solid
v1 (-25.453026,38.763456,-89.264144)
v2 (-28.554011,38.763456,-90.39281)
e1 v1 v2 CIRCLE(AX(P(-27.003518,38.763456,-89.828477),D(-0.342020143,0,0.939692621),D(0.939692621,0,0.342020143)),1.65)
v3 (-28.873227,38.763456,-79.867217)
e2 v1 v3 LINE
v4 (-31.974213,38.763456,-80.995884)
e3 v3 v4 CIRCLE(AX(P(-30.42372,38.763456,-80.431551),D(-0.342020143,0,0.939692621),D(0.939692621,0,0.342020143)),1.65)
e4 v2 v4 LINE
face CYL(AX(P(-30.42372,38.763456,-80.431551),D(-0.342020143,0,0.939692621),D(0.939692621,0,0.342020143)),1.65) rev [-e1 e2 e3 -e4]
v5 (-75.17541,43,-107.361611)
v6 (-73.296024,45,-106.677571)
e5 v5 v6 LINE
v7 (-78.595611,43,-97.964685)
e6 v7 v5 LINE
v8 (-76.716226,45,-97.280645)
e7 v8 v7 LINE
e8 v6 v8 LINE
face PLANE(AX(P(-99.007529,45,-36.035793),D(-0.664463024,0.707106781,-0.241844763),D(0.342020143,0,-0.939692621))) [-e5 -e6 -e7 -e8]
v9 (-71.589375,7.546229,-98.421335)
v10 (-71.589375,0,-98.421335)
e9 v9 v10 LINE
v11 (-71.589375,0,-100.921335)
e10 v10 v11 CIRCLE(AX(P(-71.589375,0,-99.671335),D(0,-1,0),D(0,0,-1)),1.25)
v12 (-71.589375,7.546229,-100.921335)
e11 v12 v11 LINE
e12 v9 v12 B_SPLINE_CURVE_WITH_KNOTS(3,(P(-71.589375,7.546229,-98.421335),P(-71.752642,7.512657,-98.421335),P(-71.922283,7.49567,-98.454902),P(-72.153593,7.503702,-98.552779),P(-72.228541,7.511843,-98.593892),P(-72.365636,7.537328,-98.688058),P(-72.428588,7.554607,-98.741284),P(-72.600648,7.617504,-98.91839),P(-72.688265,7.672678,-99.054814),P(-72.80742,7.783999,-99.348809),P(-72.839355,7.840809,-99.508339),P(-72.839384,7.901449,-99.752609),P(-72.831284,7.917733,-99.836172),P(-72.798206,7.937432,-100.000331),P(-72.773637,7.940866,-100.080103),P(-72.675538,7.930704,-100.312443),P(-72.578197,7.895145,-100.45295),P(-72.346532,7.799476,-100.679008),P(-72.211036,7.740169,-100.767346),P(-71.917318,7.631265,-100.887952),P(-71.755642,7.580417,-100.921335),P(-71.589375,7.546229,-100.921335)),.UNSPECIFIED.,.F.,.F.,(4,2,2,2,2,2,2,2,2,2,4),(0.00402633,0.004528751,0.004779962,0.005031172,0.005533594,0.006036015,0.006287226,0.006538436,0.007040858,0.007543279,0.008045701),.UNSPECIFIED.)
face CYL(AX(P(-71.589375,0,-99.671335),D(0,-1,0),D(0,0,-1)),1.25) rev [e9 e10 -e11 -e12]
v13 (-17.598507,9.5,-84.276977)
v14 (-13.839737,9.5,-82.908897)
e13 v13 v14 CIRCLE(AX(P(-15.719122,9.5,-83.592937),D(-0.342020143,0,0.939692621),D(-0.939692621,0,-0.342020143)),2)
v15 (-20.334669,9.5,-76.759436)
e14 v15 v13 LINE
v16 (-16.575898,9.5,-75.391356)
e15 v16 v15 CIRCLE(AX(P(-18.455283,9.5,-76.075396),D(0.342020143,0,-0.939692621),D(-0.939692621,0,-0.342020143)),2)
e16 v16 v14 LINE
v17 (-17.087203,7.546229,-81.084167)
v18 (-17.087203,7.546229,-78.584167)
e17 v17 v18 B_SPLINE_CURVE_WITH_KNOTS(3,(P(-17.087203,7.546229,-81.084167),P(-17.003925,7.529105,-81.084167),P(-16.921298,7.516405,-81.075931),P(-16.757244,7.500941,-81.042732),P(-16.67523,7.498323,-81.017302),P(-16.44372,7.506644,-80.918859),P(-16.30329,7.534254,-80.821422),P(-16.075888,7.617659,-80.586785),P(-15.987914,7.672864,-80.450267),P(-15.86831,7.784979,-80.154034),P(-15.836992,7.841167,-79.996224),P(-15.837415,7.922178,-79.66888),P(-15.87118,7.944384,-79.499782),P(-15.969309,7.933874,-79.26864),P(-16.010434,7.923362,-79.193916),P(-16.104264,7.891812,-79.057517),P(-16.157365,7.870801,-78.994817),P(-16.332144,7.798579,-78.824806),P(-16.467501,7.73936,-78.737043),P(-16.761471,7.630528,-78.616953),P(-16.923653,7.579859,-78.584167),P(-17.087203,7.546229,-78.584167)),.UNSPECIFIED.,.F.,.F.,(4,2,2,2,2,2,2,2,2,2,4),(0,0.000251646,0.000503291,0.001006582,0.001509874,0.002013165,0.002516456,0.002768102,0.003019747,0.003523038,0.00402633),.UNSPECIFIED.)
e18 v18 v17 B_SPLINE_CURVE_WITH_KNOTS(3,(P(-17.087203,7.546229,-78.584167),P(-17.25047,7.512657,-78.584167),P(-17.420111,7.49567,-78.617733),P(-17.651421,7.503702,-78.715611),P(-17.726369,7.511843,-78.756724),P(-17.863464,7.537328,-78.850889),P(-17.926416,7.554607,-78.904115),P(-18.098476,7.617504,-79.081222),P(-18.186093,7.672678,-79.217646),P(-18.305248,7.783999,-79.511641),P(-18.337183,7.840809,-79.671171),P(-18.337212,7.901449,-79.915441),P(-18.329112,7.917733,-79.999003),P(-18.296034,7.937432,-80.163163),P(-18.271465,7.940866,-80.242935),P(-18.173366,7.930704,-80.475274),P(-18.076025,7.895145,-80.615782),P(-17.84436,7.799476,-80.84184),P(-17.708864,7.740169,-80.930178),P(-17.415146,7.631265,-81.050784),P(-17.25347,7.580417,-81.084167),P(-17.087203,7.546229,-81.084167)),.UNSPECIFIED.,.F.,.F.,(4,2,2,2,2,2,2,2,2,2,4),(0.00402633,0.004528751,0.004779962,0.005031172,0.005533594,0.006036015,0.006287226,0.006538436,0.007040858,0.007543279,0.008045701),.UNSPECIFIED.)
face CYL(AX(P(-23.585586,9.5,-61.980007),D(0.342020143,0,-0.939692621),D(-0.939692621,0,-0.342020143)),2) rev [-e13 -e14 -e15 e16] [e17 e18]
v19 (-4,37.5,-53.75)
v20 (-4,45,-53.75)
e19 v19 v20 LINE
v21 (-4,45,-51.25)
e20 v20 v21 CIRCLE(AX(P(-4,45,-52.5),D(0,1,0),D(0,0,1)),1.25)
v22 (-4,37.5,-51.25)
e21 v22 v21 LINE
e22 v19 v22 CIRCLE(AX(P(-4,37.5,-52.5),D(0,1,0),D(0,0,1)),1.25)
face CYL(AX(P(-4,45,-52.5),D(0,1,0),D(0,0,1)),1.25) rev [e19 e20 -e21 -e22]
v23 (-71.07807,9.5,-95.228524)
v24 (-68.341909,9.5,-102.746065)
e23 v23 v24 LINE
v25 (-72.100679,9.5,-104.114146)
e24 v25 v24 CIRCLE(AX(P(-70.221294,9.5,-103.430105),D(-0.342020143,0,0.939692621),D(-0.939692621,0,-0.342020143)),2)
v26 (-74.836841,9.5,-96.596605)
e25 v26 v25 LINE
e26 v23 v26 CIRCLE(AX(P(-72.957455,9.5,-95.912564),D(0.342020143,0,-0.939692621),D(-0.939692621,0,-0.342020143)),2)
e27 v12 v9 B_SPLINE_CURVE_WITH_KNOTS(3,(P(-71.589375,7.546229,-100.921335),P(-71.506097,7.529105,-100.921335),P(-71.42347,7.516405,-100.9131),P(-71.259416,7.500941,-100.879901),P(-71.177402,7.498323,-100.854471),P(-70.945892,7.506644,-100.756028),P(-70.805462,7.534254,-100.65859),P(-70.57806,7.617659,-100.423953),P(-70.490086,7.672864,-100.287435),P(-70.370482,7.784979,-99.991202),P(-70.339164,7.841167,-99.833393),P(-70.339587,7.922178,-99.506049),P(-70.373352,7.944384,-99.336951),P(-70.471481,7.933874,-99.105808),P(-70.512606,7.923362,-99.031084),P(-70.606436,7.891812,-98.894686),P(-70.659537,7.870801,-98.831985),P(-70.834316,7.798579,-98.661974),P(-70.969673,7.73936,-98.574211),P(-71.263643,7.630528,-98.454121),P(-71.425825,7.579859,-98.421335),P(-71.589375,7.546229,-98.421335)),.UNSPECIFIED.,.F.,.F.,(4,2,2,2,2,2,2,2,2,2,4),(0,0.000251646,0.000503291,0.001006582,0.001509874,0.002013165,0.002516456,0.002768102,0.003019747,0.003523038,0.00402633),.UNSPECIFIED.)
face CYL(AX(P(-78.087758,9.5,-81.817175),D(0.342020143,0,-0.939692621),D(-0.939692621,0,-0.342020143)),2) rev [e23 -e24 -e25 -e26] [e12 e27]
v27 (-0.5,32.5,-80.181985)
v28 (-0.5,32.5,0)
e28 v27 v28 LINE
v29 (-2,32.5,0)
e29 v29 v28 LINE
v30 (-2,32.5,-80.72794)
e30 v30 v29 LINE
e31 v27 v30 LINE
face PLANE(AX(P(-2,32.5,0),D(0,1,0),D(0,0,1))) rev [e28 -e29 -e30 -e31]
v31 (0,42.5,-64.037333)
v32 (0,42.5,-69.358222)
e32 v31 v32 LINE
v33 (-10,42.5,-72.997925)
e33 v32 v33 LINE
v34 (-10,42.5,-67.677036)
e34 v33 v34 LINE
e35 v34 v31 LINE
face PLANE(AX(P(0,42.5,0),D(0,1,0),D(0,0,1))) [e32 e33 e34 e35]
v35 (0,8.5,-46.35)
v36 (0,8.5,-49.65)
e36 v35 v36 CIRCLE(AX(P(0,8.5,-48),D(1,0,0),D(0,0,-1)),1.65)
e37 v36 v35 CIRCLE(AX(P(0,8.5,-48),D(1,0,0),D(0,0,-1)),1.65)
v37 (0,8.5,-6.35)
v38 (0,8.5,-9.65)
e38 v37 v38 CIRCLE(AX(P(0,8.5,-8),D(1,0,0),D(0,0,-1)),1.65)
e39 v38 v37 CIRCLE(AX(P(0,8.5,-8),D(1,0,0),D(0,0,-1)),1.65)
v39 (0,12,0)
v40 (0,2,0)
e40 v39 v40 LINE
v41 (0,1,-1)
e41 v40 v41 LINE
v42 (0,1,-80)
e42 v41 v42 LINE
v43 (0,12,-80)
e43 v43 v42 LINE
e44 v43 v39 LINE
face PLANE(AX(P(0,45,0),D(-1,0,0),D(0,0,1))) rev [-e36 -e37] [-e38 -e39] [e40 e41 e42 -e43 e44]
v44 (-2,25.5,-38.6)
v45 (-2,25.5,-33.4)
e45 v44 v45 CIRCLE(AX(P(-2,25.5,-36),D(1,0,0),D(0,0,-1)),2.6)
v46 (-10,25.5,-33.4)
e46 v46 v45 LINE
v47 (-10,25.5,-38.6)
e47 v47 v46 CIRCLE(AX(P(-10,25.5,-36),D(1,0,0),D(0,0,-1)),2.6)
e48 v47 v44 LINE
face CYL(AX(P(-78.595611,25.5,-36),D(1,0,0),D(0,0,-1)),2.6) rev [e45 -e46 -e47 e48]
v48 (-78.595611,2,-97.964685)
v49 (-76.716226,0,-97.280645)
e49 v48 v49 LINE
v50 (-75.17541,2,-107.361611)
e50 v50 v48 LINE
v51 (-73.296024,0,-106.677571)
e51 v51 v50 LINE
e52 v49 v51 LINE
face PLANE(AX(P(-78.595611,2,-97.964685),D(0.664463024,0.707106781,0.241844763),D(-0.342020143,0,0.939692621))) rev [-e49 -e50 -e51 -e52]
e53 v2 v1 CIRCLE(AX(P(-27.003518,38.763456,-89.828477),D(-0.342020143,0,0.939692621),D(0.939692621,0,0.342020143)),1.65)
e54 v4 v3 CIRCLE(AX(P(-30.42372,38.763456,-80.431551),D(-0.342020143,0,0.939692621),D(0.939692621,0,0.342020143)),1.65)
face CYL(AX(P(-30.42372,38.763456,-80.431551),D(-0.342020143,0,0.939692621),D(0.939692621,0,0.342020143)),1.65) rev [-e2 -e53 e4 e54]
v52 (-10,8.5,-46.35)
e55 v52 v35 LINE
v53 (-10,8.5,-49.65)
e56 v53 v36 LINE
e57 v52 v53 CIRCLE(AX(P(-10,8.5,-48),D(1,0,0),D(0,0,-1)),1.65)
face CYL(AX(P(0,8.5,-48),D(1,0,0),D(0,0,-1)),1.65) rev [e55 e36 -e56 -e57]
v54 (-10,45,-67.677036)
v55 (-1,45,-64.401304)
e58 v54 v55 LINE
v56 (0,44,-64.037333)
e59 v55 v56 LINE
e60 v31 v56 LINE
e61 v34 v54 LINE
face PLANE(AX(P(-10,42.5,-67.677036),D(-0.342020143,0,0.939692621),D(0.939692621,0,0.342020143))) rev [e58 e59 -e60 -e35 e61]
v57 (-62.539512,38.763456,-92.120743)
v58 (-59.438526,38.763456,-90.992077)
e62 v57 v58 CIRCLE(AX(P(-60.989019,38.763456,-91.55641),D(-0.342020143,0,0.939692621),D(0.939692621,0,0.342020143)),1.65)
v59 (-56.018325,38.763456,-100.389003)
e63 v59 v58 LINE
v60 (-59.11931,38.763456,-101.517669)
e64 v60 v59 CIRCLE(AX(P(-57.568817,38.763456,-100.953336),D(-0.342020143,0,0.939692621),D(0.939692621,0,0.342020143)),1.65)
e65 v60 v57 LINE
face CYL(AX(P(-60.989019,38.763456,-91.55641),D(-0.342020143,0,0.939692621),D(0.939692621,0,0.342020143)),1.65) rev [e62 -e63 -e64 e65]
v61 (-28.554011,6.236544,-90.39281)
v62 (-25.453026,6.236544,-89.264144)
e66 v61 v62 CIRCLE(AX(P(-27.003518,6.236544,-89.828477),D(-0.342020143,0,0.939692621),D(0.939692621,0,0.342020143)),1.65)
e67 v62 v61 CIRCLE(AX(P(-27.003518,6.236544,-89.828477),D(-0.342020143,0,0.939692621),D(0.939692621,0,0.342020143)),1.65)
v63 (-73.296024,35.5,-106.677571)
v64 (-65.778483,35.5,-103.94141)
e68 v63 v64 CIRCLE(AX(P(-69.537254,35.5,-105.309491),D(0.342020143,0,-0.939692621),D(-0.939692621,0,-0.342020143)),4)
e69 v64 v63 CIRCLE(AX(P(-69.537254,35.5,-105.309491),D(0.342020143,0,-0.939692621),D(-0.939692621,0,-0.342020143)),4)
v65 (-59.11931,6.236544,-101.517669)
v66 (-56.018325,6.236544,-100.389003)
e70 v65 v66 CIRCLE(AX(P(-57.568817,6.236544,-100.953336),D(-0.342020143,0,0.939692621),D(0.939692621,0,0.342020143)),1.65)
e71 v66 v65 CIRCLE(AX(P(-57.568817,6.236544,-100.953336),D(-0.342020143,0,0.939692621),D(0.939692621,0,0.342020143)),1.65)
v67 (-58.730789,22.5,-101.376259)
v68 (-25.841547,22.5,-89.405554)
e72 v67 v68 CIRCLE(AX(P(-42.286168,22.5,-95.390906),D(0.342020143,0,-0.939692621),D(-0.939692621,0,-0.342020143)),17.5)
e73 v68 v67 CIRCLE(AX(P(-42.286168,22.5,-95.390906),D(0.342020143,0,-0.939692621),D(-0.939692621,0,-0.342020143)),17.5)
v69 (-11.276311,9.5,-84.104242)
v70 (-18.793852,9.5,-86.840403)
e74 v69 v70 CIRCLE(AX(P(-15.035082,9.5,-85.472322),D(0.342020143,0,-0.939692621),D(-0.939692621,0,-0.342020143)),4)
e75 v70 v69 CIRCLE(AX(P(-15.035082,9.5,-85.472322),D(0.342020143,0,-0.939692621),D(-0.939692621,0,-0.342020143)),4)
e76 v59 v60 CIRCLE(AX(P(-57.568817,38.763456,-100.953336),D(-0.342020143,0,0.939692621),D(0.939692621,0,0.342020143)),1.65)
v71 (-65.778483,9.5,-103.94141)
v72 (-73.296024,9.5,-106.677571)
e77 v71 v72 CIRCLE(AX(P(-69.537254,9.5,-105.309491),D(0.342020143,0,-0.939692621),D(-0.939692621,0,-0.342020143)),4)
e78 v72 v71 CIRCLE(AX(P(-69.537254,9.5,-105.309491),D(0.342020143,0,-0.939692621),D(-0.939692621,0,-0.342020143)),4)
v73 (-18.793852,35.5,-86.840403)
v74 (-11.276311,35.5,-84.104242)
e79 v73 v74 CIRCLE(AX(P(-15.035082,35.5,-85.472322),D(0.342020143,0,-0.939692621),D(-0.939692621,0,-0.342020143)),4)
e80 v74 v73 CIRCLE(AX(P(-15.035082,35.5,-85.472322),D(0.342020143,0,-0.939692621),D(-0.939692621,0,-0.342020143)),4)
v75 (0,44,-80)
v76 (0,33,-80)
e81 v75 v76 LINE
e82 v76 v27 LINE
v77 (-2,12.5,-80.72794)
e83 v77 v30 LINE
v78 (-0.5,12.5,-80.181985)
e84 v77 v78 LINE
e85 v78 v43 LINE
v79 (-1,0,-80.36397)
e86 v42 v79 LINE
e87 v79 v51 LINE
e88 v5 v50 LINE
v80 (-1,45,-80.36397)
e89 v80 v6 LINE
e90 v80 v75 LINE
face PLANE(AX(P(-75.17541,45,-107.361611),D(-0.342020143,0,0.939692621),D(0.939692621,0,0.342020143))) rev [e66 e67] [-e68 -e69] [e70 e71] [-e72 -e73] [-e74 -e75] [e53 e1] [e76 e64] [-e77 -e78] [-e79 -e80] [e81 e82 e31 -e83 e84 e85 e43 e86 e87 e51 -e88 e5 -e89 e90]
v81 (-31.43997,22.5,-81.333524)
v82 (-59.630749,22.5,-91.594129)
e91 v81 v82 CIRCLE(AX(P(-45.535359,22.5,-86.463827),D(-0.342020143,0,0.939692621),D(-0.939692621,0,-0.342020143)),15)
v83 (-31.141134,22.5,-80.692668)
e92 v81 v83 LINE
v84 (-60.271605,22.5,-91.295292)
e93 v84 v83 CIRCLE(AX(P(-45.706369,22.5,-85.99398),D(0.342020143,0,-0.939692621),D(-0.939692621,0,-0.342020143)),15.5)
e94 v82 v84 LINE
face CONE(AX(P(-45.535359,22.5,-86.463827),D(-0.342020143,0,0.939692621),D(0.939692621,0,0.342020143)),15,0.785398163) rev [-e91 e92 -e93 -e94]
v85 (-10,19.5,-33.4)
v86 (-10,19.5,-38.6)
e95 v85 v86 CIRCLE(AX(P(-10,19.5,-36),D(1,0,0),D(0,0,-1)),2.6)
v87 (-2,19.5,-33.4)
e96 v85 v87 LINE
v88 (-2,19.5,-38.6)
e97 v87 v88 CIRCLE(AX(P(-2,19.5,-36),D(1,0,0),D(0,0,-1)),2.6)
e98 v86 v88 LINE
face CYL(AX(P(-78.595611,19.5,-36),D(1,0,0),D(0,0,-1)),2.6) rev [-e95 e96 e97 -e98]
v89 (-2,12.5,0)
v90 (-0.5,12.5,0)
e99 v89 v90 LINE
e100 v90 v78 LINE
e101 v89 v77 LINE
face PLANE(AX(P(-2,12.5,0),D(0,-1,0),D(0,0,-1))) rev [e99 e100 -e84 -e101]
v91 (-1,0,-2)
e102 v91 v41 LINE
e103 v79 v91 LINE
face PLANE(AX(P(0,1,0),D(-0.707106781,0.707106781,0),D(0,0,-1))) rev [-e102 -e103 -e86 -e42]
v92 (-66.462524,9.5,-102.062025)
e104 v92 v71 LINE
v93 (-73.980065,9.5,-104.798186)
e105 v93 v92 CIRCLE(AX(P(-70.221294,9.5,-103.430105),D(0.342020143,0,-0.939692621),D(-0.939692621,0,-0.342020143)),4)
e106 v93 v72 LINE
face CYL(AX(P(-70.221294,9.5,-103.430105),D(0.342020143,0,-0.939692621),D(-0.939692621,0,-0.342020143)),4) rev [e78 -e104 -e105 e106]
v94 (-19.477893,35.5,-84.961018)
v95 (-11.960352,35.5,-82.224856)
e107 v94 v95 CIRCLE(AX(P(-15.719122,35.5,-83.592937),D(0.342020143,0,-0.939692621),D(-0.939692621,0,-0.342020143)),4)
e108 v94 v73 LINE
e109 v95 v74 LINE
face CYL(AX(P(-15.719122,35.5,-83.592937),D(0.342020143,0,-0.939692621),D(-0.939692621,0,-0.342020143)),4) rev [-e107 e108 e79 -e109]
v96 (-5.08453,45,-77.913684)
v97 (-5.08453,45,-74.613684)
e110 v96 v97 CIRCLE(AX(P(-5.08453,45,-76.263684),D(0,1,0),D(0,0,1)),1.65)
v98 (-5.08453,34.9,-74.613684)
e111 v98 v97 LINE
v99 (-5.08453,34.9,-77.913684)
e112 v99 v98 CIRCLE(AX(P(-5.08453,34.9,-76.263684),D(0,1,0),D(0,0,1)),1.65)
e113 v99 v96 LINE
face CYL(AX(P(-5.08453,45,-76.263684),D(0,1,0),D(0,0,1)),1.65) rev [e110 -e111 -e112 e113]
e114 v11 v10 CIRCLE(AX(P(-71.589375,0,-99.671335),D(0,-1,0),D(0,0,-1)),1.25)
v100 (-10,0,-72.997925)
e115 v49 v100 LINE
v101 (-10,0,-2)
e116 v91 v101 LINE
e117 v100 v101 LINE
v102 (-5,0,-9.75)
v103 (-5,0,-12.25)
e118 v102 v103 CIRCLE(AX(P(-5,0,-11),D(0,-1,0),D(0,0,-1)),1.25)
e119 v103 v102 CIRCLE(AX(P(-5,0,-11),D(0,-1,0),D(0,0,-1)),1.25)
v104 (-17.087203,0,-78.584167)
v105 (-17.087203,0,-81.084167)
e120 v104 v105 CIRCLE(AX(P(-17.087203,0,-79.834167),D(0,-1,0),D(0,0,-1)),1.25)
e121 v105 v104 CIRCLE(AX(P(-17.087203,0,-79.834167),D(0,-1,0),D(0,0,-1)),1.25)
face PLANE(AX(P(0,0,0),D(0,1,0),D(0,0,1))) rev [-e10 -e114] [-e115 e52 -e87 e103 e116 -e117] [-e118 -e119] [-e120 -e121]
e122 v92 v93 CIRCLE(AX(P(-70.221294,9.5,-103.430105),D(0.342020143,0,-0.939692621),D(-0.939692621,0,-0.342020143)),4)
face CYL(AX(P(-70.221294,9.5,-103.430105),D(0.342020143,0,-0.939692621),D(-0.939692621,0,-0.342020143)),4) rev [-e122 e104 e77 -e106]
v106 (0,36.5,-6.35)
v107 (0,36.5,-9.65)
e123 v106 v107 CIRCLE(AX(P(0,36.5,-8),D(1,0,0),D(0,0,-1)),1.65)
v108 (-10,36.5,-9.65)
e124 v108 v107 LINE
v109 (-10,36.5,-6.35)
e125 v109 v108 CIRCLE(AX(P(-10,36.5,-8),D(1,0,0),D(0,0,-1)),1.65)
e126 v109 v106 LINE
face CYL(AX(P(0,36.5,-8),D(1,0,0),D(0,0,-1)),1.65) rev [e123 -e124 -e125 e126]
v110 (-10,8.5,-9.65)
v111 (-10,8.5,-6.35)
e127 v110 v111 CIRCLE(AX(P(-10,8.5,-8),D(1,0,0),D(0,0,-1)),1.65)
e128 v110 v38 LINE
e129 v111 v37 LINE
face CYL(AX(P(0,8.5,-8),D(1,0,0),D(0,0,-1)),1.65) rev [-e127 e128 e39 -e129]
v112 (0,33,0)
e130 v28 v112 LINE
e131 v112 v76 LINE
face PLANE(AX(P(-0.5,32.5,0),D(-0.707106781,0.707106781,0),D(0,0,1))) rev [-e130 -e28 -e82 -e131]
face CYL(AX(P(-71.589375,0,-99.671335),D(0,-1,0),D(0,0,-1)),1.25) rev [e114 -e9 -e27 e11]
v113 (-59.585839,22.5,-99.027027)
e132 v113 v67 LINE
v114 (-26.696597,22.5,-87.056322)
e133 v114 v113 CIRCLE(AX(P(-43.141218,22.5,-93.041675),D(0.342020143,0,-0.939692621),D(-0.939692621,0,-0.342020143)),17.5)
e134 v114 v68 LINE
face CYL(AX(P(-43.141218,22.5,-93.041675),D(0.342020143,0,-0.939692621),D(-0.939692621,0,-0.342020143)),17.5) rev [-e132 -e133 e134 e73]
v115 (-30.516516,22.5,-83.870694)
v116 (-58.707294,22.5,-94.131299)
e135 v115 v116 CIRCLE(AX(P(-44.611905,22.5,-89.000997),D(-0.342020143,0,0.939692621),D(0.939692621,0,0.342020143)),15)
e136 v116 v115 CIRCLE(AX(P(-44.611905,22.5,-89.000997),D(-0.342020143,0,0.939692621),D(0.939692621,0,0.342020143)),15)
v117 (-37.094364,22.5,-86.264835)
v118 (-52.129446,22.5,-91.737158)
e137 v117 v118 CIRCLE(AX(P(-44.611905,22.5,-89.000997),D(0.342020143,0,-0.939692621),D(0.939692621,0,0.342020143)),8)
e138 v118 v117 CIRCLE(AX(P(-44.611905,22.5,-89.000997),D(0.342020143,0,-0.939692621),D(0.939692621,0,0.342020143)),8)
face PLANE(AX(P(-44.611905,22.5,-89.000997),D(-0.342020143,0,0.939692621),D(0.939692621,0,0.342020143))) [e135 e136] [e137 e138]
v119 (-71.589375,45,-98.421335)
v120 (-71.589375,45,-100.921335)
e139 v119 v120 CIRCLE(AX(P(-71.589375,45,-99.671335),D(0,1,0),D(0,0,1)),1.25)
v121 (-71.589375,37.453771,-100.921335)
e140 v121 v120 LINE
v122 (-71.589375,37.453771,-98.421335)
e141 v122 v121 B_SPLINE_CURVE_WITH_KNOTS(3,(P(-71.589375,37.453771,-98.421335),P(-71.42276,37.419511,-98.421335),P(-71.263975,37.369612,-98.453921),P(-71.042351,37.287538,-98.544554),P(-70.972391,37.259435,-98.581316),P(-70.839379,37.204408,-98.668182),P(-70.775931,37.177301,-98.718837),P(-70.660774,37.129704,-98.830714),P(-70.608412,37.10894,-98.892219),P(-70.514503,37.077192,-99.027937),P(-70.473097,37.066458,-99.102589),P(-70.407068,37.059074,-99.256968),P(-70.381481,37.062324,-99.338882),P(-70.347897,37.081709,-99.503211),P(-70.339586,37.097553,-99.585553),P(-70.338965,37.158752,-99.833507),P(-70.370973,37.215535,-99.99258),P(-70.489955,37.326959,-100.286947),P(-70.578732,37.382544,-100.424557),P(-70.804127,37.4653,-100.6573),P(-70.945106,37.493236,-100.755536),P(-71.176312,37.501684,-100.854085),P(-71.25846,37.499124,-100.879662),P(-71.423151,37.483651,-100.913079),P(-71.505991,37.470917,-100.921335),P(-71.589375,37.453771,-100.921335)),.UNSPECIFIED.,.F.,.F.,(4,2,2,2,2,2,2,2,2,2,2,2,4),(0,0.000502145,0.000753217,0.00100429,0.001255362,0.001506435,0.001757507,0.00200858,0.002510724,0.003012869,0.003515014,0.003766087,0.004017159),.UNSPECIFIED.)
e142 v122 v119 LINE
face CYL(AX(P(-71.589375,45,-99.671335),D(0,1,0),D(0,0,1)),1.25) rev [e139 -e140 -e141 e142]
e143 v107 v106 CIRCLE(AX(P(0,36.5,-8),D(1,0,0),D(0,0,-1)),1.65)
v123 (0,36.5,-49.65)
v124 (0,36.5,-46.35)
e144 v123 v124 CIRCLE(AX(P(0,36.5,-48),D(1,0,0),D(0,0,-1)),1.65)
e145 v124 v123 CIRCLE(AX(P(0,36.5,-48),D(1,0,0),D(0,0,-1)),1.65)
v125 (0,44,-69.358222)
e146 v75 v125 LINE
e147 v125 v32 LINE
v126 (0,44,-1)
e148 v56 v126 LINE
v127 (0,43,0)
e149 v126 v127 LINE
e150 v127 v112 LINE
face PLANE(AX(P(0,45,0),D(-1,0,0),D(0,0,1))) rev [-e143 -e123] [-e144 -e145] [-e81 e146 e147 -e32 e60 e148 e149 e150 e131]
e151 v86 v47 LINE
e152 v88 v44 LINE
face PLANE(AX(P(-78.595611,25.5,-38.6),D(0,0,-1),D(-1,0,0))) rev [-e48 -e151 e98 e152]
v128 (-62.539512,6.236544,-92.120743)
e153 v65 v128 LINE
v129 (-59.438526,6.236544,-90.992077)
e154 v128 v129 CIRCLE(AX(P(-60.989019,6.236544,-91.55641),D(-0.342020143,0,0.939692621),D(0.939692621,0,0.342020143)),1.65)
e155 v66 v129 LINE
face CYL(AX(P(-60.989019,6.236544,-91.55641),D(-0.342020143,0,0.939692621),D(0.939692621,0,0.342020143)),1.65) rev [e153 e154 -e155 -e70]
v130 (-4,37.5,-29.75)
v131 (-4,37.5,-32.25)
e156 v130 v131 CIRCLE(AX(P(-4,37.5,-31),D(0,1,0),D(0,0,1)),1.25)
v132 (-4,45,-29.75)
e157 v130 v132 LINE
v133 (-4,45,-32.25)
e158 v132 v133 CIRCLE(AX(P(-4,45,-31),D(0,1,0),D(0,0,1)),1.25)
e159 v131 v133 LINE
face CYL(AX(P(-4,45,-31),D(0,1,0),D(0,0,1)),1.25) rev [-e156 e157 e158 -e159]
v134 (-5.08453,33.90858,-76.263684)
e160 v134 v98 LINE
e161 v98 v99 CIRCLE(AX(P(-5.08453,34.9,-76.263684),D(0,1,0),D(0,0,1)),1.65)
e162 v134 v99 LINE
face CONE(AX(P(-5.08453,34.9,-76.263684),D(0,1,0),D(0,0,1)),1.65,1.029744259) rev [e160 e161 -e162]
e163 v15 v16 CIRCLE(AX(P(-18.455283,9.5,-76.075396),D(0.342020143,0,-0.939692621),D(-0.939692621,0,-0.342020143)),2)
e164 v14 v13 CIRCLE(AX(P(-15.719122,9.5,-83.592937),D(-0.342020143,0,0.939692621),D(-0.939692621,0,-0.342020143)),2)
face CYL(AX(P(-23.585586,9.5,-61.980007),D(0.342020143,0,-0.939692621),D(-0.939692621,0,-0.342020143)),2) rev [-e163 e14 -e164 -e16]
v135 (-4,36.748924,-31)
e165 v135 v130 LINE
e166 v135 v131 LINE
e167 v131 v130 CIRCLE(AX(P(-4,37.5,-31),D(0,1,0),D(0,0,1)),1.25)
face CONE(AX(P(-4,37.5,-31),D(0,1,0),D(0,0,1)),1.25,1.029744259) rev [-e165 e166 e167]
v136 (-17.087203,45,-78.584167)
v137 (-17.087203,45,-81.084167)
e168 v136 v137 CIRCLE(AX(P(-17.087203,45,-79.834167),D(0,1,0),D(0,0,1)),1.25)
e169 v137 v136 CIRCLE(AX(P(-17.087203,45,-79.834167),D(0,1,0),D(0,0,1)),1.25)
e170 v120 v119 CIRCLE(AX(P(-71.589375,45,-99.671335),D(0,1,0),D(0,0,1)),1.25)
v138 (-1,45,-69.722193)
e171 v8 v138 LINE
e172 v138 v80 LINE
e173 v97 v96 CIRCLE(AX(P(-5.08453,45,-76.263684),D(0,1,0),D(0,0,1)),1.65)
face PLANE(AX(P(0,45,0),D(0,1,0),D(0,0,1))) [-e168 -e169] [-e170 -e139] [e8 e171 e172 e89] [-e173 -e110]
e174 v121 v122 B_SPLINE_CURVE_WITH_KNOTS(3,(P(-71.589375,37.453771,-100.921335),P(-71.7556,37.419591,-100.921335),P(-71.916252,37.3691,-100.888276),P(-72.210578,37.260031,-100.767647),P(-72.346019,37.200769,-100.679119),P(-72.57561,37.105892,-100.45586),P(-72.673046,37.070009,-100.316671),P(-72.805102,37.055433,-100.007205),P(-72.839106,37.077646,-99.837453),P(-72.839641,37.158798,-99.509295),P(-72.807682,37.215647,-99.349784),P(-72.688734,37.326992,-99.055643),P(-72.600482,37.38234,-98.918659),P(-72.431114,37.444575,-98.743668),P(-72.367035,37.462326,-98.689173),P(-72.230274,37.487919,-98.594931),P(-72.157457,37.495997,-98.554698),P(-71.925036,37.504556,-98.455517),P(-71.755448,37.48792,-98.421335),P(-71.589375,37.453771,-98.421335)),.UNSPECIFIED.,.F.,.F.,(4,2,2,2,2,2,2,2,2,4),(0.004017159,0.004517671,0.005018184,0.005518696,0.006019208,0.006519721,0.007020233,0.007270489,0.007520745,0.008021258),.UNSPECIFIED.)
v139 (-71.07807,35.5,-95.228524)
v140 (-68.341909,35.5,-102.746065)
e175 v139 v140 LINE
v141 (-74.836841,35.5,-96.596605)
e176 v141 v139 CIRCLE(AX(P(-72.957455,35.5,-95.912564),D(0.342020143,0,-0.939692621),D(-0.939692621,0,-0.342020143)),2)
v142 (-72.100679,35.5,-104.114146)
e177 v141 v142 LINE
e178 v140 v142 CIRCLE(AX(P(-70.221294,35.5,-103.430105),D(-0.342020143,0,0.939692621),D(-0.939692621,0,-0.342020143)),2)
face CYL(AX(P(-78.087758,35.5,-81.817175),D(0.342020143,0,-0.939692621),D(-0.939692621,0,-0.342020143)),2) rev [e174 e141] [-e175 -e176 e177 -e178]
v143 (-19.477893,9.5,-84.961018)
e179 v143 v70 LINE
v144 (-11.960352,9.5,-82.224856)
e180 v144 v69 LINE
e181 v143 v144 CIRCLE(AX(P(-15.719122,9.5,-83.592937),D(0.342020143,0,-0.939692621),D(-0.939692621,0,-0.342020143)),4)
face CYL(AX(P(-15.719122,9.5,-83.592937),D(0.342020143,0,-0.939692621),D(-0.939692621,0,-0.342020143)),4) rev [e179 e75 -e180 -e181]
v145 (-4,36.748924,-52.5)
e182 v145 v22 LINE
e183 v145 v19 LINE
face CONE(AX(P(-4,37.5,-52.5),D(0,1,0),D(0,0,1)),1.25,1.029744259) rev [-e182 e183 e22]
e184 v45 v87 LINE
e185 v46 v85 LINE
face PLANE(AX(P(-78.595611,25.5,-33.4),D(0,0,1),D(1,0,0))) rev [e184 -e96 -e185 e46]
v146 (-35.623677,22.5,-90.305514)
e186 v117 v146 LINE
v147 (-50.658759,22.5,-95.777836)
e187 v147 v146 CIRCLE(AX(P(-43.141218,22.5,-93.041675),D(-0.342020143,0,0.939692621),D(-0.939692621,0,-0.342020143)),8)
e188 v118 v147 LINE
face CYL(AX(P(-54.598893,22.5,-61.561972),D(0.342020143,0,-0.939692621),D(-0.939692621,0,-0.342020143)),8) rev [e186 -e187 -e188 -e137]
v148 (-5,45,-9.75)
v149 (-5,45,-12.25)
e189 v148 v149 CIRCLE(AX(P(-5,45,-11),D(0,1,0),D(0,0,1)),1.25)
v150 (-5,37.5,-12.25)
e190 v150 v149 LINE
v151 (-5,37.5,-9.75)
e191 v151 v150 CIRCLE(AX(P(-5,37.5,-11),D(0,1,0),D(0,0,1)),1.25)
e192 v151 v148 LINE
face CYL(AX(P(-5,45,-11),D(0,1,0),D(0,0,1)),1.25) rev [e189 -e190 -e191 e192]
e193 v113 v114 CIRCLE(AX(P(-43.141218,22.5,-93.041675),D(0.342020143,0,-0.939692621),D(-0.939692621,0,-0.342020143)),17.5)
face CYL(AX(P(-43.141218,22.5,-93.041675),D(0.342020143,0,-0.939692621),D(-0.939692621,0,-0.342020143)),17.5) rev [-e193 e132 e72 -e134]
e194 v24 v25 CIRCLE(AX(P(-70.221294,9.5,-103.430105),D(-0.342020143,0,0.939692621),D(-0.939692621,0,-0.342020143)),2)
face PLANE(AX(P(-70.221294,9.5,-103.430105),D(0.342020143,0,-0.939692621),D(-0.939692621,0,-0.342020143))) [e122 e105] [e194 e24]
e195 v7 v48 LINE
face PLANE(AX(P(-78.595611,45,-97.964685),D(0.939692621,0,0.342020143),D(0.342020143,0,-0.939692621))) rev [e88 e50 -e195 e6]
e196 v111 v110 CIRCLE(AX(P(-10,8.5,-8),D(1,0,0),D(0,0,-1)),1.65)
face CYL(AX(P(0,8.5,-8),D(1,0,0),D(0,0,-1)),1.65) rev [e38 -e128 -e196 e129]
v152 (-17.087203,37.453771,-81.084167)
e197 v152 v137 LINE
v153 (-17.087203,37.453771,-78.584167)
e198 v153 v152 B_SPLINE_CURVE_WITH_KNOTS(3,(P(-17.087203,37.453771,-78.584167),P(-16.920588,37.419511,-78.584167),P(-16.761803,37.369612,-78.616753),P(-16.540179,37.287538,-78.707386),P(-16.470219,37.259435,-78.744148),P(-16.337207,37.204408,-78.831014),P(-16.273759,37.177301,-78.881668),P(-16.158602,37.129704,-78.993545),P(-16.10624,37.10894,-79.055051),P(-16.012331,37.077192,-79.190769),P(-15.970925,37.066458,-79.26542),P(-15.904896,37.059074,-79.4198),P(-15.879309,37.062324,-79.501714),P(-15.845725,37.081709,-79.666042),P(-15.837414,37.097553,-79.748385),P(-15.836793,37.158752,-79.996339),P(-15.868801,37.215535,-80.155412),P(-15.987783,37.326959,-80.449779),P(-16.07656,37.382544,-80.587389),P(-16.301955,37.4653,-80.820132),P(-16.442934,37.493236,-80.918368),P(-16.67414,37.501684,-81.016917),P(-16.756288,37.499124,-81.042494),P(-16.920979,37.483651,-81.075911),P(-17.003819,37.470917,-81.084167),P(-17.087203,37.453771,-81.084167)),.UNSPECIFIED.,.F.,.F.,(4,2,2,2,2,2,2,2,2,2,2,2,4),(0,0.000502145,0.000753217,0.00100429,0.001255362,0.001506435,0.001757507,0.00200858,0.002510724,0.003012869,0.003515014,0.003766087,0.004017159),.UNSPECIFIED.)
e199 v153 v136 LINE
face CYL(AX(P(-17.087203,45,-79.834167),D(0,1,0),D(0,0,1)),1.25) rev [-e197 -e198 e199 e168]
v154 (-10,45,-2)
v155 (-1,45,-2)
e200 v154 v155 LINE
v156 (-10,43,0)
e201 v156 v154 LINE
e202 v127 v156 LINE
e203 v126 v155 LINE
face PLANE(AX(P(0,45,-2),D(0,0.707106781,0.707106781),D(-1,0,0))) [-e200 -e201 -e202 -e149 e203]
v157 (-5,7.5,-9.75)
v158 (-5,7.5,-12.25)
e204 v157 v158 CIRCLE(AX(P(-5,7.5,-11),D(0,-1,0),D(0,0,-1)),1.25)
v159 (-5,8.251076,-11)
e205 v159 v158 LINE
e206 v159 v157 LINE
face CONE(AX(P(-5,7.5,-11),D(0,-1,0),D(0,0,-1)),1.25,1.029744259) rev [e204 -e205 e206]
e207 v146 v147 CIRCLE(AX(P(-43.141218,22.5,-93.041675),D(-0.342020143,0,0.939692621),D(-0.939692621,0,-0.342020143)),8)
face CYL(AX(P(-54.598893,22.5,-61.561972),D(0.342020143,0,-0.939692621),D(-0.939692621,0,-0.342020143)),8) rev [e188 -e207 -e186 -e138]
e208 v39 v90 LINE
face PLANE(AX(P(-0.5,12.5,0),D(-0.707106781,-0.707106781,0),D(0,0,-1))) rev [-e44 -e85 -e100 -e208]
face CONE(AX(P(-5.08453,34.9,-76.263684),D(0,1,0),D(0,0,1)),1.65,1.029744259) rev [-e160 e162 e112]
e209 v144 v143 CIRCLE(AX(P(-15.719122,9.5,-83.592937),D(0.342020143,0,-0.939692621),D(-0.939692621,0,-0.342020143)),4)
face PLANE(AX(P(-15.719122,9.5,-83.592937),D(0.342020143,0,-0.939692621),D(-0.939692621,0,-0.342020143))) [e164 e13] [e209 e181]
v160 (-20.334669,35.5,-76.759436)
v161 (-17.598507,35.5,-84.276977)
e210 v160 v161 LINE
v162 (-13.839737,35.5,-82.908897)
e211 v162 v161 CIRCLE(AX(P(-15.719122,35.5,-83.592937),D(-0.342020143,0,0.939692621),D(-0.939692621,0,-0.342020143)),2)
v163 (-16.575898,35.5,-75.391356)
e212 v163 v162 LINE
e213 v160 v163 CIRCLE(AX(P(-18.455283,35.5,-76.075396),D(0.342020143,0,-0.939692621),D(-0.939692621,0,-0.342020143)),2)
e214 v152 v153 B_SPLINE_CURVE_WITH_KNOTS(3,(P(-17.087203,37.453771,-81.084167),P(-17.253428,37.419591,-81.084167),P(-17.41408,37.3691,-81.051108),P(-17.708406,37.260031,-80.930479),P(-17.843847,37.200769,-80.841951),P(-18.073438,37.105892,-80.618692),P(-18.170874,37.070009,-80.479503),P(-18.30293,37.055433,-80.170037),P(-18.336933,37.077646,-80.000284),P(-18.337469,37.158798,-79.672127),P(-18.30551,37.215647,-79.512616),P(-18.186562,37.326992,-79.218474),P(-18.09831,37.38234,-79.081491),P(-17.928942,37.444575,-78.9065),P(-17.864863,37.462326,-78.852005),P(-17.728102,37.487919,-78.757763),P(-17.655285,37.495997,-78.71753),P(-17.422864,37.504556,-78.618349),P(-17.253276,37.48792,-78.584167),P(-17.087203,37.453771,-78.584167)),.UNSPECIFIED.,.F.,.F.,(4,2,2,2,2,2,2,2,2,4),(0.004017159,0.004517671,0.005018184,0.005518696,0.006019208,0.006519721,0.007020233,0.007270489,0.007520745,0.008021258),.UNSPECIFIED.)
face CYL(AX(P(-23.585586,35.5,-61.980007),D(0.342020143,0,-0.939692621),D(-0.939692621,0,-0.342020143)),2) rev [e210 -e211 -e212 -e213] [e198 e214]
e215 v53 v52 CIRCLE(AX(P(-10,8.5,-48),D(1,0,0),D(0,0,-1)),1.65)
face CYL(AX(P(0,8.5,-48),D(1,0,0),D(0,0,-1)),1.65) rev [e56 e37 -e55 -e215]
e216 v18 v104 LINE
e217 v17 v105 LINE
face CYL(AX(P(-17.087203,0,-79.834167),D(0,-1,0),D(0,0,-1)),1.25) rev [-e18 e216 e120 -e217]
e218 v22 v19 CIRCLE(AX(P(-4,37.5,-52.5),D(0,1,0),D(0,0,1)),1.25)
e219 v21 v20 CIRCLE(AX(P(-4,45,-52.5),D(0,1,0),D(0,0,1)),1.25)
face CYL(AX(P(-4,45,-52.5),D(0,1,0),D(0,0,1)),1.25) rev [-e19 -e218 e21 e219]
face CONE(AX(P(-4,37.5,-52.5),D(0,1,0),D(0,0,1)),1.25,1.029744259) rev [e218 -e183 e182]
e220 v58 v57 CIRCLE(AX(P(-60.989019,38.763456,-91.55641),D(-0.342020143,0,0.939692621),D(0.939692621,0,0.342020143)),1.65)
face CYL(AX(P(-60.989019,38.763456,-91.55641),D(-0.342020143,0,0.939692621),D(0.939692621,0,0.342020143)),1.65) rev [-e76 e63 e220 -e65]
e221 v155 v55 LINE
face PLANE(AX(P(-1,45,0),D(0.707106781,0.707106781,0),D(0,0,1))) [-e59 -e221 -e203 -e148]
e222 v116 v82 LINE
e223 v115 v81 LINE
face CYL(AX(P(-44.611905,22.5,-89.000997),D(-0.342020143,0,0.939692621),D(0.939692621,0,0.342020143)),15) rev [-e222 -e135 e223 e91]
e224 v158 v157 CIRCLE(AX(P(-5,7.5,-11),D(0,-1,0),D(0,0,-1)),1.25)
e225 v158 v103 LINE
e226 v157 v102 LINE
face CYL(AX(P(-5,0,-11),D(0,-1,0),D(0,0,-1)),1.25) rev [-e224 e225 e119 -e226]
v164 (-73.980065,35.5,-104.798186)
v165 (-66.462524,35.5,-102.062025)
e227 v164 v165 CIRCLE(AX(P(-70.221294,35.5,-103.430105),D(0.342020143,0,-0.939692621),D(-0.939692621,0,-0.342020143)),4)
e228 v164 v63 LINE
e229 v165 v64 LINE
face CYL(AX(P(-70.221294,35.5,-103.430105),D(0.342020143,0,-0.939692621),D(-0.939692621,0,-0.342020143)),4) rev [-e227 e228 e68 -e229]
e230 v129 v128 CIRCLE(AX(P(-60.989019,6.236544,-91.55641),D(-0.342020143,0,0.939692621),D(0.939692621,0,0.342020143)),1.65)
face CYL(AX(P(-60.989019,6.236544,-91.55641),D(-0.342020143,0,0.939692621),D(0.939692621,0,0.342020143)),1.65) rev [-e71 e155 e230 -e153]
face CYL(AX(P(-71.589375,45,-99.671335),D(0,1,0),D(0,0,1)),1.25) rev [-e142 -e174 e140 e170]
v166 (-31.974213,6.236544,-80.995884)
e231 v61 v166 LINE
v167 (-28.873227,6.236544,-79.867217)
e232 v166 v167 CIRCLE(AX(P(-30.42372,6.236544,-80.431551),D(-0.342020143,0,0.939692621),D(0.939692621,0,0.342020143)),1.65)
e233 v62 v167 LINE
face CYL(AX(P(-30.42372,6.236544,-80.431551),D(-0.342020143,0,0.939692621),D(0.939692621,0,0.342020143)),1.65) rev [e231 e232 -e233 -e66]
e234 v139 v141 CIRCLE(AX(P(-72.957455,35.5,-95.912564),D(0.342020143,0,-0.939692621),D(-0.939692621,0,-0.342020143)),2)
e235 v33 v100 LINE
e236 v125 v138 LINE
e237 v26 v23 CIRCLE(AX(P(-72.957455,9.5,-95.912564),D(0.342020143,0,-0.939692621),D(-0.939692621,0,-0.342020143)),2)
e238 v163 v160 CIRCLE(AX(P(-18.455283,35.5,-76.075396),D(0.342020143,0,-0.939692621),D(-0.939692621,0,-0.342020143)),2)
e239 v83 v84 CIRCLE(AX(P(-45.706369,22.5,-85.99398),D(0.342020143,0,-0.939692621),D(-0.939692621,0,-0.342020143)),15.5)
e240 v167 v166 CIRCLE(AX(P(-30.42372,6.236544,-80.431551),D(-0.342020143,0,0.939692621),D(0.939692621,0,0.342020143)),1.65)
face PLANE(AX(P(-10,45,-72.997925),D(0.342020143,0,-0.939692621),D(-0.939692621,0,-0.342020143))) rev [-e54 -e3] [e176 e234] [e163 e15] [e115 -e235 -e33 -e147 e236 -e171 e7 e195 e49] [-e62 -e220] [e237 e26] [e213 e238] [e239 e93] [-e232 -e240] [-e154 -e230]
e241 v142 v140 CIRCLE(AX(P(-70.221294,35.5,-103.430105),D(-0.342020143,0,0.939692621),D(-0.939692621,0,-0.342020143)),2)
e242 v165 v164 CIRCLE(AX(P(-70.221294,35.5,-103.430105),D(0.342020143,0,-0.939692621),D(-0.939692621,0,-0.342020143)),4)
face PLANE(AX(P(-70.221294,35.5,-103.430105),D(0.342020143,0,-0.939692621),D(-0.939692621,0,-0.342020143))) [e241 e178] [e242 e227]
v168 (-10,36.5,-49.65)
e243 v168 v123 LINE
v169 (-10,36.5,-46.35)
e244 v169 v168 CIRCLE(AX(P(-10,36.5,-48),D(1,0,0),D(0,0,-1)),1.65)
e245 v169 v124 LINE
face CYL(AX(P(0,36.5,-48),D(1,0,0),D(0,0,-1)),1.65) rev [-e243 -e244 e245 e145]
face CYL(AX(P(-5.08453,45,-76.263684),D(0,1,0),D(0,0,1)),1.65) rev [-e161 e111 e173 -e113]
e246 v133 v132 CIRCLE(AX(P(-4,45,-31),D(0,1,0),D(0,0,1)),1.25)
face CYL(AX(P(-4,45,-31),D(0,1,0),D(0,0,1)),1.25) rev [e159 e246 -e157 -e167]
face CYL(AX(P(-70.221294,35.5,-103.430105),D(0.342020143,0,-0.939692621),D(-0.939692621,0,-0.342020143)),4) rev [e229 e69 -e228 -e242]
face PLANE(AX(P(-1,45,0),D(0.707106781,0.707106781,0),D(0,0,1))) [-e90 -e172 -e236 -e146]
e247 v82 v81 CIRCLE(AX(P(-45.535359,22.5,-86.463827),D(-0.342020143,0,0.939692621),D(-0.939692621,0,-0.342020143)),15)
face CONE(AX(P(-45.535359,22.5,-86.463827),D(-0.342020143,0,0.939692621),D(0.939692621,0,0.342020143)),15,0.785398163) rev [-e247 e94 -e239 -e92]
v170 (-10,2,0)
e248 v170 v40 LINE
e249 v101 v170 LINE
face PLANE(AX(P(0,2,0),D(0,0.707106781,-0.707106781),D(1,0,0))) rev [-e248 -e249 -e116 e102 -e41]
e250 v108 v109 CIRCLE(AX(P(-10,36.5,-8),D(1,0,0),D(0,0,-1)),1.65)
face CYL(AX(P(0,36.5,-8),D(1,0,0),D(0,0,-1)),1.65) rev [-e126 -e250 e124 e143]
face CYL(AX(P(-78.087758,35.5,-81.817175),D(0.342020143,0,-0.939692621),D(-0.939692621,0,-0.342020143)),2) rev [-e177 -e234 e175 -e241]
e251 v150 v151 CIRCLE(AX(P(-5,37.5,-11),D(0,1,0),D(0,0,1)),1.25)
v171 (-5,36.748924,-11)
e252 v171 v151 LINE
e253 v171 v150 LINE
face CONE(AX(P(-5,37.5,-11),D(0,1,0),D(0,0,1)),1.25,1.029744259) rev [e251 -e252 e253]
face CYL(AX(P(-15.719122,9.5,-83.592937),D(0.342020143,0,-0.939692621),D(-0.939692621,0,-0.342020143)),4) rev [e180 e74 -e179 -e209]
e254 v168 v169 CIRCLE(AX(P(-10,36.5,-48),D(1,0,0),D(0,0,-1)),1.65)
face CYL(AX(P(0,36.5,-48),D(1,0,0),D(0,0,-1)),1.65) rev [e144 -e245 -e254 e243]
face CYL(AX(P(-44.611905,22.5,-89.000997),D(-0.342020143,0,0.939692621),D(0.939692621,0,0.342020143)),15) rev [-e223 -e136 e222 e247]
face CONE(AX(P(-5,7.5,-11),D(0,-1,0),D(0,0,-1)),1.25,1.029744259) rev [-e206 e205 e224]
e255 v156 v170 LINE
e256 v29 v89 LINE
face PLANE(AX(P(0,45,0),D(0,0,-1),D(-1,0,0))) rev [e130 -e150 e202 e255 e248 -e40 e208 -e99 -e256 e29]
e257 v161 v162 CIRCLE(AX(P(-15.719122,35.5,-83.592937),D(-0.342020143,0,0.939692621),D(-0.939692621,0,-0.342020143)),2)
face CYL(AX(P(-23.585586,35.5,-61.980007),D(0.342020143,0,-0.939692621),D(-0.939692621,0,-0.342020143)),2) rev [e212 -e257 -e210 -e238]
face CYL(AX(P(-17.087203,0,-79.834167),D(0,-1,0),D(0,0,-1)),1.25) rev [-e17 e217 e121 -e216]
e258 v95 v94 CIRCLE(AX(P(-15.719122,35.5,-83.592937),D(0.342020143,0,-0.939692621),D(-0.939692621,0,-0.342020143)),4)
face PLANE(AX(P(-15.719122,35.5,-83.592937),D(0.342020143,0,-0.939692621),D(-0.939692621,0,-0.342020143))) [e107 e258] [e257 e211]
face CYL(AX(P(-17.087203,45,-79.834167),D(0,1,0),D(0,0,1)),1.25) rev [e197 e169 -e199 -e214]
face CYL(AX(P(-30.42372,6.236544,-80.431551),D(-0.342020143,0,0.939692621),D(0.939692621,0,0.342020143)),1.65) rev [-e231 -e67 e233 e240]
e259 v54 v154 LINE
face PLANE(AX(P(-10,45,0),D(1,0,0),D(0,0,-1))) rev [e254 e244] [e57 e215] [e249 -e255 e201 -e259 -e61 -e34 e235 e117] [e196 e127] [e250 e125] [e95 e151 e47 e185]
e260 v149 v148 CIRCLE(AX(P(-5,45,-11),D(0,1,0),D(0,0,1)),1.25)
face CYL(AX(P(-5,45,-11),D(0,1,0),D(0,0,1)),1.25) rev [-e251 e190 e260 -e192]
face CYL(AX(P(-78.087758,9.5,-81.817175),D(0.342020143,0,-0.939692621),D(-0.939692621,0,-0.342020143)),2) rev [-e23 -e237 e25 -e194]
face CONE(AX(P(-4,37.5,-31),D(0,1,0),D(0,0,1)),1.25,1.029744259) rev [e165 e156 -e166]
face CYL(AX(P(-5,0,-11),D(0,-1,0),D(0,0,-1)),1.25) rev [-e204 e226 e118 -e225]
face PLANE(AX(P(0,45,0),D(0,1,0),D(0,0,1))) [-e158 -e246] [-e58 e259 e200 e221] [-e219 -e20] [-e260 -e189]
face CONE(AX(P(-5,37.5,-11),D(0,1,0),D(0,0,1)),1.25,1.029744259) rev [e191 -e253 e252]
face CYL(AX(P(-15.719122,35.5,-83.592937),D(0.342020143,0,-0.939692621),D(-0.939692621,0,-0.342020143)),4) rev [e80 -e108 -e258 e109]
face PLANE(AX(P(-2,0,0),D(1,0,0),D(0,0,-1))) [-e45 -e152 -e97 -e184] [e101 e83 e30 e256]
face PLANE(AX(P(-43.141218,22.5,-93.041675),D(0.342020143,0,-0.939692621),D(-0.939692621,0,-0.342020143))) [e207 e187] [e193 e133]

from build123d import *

# Parameters (mm, degrees)
BOSS_EXTRUDE1_DEPTH        = 45
SKETCH2_R                  = 8
CUT_EXTRUDE1_DEPTH         = 36
SKETCH3_R                  = 15
CUT_EXTRUDE2_DEPTH         = 3.2
SKETCH4_R                  = 2
CUT_EXTRUDE3_DEPTH         = 25
SKETCH5_R                  = 4
CUT_EXTRUDE4_DEPTH         = 2
SKETCH7_R                  = 1
CUT_EXTRUDE5_DEPTH         = 8
M3_TAPPED_HOLE1_AT_2_COUNT = 2
M3_TAPPED_HOLE1_AT_2_PITCH = 58
SKETCH13_R                 = 17.5
CUT_EXTRUDE8_DEPTH         = 2.5
CUT_EXTRUDE9_DEPTH         = 2.5
M4_TAPPED_HOLE2_D          = 3.3
M4_TAPPED_HOLE2_DEPTH      = 10.1
M4_TAPPED_HOLE2_TIP        = 0.991420021
CHAMFER1_SIZE              = 2
M4_TAPPED_HOLE3_D          = 3.3
M4_TAPPED_HOLE3_DEPTH      = 10.1
M4_TAPPED_HOLE3_TIP        = 0.991420021
M3_TAPPED_HOLE2_D          = 2.5
M3_TAPPED_HOLE2_DEPTH      = 7.5
M3_TAPPED_HOLE2_TIP        = 0.751075774
SKETCH9_W                  = 82.200084453
SKETCH9_H                  = 20
CUT_EXTRUDE10_DEPTH        = 2
CUT_EXTRUDE11_DEPTH        = 140.349930982
CHAMFER2_SIZE              = 1
CHAMFER3_SIZE              = 0.5
M4_TAPPED_HOLE4_D          = 3.3
CIRPATTERN1_COUNT          = 4
CHAMFER4_SIZE              = 0.5


with BuildPart() as part:
    # Sketch1 → Boss-Extrude1 (new body)
    with BuildSketch(Plane(origin=(0, 0, 0), x_dir=(1, 0, 0), z_dir=(0, 1, 0))):
        Polygon((-75.175409663, 107.361611466), (0, 80), (0, 0), (-10, 0), (-10, 72.997924618), (-78.595611096, 97.964685258), align=None)
    extrude(amount=BOSS_EXTRUDE1_DEPTH)

    # Sketch2 → Cut-Extrude1 (cut)
    with BuildSketch(Plane(origin=(25.711504387, 0, -70.641777725), x_dir=(-0.9396926207859106, 0, -0.3420201433256628), z_dir=(0.3420201433256628, 0, -0.9396926207859106))):
        with Locations((72.361611466, 22.5)):
            Circle(SKETCH2_R)
    extrude(amount=-CUT_EXTRUDE1_DEPTH, mode=Mode.SUBTRACT)

    # Sketch3 → Cut-Extrude2 (cut)
    with BuildSketch(Plane(origin=(22.291302954, 0, -61.244851517), x_dir=(0.9396926207859108, 0, 0.34202014332566244), z_dir=(-0.34202014332566244, 0, 0.9396926207859108))):
        with Locations((-72.361611466, 22.5)):
            Circle(SKETCH3_R)
    extrude(amount=-CUT_EXTRUDE2_DEPTH, mode=Mode.SUBTRACT)

    # Sketch4 → Cut-Extrude3 (cut)
    with BuildSketch(Plane(origin=(25.711504387, 0, -70.641777725), x_dir=(-0.9396926207859106, 0, -0.3420201433256628), z_dir=(0.3420201433256628, 0, -0.9396926207859106))):
        with Locations((43.361611466, 35.5)):
            Circle(SKETCH4_R)
        with Locations((101.361611466, 35.5)):
            Circle(SKETCH4_R)
        with Locations((101.361611466, 9.5)):
            Circle(SKETCH4_R)
        with Locations((43.361611466, 9.5)):
            Circle(SKETCH4_R)
    extrude(amount=-CUT_EXTRUDE3_DEPTH, mode=Mode.SUBTRACT)

    # Sketch5 → Cut-Extrude4 (cut)
    with BuildSketch(Plane(origin=(25.711504387, 0, -70.641777725), x_dir=(-0.9396926207859106, 0, -0.3420201433256628), z_dir=(0.3420201433256628, 0, -0.9396926207859106))):
        with Locations((43.361611466, 35.5)):
            Circle(SKETCH5_R)
        with Locations((43.361611466, 9.5)):
            Circle(SKETCH5_R)
        with Locations((101.361611466, 9.5)):
            Circle(SKETCH5_R)
        with Locations((101.361611466, 35.5)):
            Circle(SKETCH5_R)
    extrude(amount=-CUT_EXTRUDE4_DEPTH, mode=Mode.SUBTRACT)

    # Sketch7 → Cut-Extrude5 (cut)
    with BuildSketch(Plane.XZ):
        with Locations(Location((-71.589374798, -99.671334881, 0), (0, 0, 270))):
            Circle(SKETCH7_R)
        with Locations(Location((-17.087202793, -79.834166568, 0), (0, 0, 270))):
            Circle(SKETCH7_R)
    extrude(amount=-CUT_EXTRUDE5_DEPTH, mode=Mode.SUBTRACT)

    # Sketch8 → M3 Tapped Hole1 (revolve, cut)
    with BuildSketch(Plane(origin=(-17.087202793, 0, -79.834166568), x_dir=(0, 0, -1), z_dir=(1, 0, 0))):
        Polygon((0, 0), (0, 10.251075774), (1.25, 9.5), (1.25, 0), align=None)
    m3_tapped_hole1 = revolve(axis=Axis((-17.087202793, -6.35, -79.834166568), (0, 1, 0)), mode=Mode.SUBTRACT)

    # M3 Tapped Hole1 at 2: M3 Tapped Hole1 ×2
    with Locations(*[Vector(-0.9396926207859108, 0, -0.3420201433256624) * (i * M3_TAPPED_HOLE1_AT_2_PITCH) for i in range(1, M3_TAPPED_HOLE1_AT_2_COUNT)]):
        add(m3_tapped_hole1, mode=Mode.SUBTRACT)

    # Mirror1: M3 Tapped Hole1 across plane
    add(m3_tapped_hole1.mirror(Plane(origin=(0, 22.5, 0), x_dir=(0, 0, 1), z_dir=(0, -1, 0))), mode=Mode.SUBTRACT)

    # Mirror1 copy 1 sketch → Mirror1 copy 1 (revolve, cut)
    with BuildSketch(Plane(origin=(-71.589374798, 45, -99.671334881), x_dir=(0, 0, -1), z_dir=(1, 0, 0))):
        Polygon((0, 0), (0, -10.251075774), (1.25, -9.5), (1.25, 0), align=None)
    revolve(axis=Axis((-71.589374798, 51.35, -99.671334881), (0, 1, 0)), mode=Mode.SUBTRACT)

    # Sketch13 → Cut-Extrude8 (cut)
    with BuildSketch(Plane(origin=(25.711504387, 0, -70.641777725), x_dir=(-0.9396926207859106, 0, -0.3420201433256628), z_dir=(0.34202014332566283, 0, -0.9396926207859106))):
        with Locations((72.361611466, 22.5)):
            Circle(SKETCH13_R)
    extrude(amount=-CUT_EXTRUDE8_DEPTH, mode=Mode.SUBTRACT)

    # Sketch15 → Cut-Extrude9 (cut)
    with BuildSketch(Plane(origin=(0, 45, 0), x_dir=(1, 0, 0), z_dir=(0, 1, 0))):
        Polygon((-10, 72.997924618), (1.8, 68.703075854), (1.8, 63.382186991), (-10, 67.677035756), align=None)
    extrude(amount=-CUT_EXTRUDE9_DEPTH, mode=Mode.SUBTRACT)

    # M4 Tapped Hole2
    with Locations(Plane(origin=(-5.084529925, 45, -76.263684243), x_dir=(0, 0, 1), z_dir=(0, 1, 0))):
        with Locations((0, 0)):
            Hole(M4_TAPPED_HOLE2_D / 2, depth=M4_TAPPED_HOLE2_DEPTH)
            with Locations((0, 0, -(M4_TAPPED_HOLE2_DEPTH + M4_TAPPED_HOLE2_TIP / 2))):  # 118° drill point
                Cone(0, M4_TAPPED_HOLE2_D / 2, M4_TAPPED_HOLE2_TIP, mode=Mode.SUBTRACT)

    # Chamfer1
    chamfer1_edges = [part.edges().sort_by_distance(p)[0] for p in [
        (-76.88551038, 45, -102.663148362),
        (-5, 45, 0),
        (-5, 0, 0),
        (-76.88551038, 0, -102.663148362),
    ]]
    chamfer(chamfer1_edges, length=CHAMFER1_SIZE)

    # M4 Tapped Hole3
    with Locations(Plane(origin=(0, 0, 0), x_dir=(0, 0, -1), z_dir=(1, 0, 0))):
        with Locations((48, 36.5), (48, 8.5), (8, 8.5), (8, 36.5)):
            Hole(M4_TAPPED_HOLE3_D / 2, depth=M4_TAPPED_HOLE3_DEPTH)
            with Locations((0, 0, -(M4_TAPPED_HOLE3_DEPTH + M4_TAPPED_HOLE3_TIP / 2))):  # 118° drill point
                Cone(0, M4_TAPPED_HOLE3_D / 2, M4_TAPPED_HOLE3_TIP, mode=Mode.SUBTRACT)

    # M3 Tapped Hole2
    with Locations(Plane(origin=(0, 45, 0), x_dir=(1, 0, 0), z_dir=(0, 1, 0))):
        with Locations((-4, 52.5), (-4, 31)):
            Hole(M3_TAPPED_HOLE2_D / 2, depth=M3_TAPPED_HOLE2_DEPTH)
            with Locations((0, 0, -(M3_TAPPED_HOLE2_DEPTH + M3_TAPPED_HOLE2_TIP / 2))):  # 118° drill point
                Cone(0, M3_TAPPED_HOLE2_D / 2, M3_TAPPED_HOLE2_TIP, mode=Mode.SUBTRACT)

    # Sketch23 → M3 Tapped Hole4 (revolve, cut)
    with BuildSketch(Plane(origin=(-5, 0, -11), x_dir=(0, 0, -1), z_dir=(1, 0, 0))):
        Polygon((0, 0), (0, 8.251075774), (1.25, 7.5), (1.25, 0), align=None)
    m3_tapped_hole4 = revolve(axis=Axis((-5, -6.35, -11), (0, 1, 0)), mode=Mode.SUBTRACT)

    # Mirror2: M3 Tapped Hole4 across plane
    add(m3_tapped_hole4.mirror(Plane(origin=(0, 22.5, 0), x_dir=(0, 0, 1), z_dir=(0, -1, 0))), mode=Mode.SUBTRACT)

    # Sketch9 → Cut-Extrude10 (cut)
    with BuildSketch(Plane(origin=(0, 0, 0), x_dir=(0, 0, -1), z_dir=(1, 0, 0))):
        with Locations((41.100042227, 22.5)):
            Rectangle(SKETCH9_W, SKETCH9_H)
    extrude(amount=-CUT_EXTRUDE10_DEPTH, mode=Mode.SUBTRACT)

    # Sketch25 → Cut-Extrude11 (cut, through all)
    with BuildSketch(Plane(origin=(-2, 0, 0), x_dir=(0, 0, -1), z_dir=(1, 0, 0))):
        with BuildLine():
            Line((38.6, 25.5), (38.6, 19.5))
            ThreePointArc((38.6, 19.5), (36, 16.9), (33.4, 19.5))
            Line((33.4, 19.5), (33.4, 25.5))
            ThreePointArc((33.4, 25.5), (36, 28.1), (38.6, 25.5))
        make_face()
    extrude(amount=-CUT_EXTRUDE11_DEPTH, mode=Mode.SUBTRACT)

    # Chamfer2
    chamfer2_edges = [part.edges().sort_by_distance(p)[0] for p in [
        (0, 45, -74.679111138),
        (0, 45, -33.018666706),
        (0, 0, -41),
    ]]
    chamfer(chamfer2_edges, length=CHAMFER2_SIZE)

    # Chamfer3
    chamfer3_edges = [part.edges().sort_by_distance(p)[0] for p in [
        (-59.80175868, 22.5, -91.124282392),
    ]]
    chamfer(chamfer3_edges, length=CHAMFER3_SIZE)

    # M4 Tapped Hole4 (through all)
    with Locations(Plane(origin=(22.291302954, 0, -61.244851517), x_dir=(0.9396926207859106, 0, 0.34202014332566244), z_dir=(-0.34202014332566244, 0, 0.9396926207859106))):
        with Locations((-88.625067433, 38.763455967)):
            m4_tapped_hole4 = Hole(M4_TAPPED_HOLE4_D / 2)

    # CirPattern1: M4 Tapped Hole4 ×4 about axis
    cirpattern1_axis = Axis((-67.997672323, 22.5, -24.749128725), (-0.34202014332566244, 0, 0.9396926207859106))
    for i in range(1, CIRPATTERN1_COUNT):
        add(m4_tapped_hole4.rotate(cirpattern1_axis, i * 360 / CIRPATTERN1_COUNT), mode=Mode.SUBTRACT)

    # Chamfer4
    chamfer4_edges = [part.edges().sort_by_distance(p)[0] for p in [
        (0, 12.5, -40),
        (0, 32.5, -40),
    ]]
    chamfer(chamfer4_edges, length=CHAMFER4_SIZE)


solid = part.part
